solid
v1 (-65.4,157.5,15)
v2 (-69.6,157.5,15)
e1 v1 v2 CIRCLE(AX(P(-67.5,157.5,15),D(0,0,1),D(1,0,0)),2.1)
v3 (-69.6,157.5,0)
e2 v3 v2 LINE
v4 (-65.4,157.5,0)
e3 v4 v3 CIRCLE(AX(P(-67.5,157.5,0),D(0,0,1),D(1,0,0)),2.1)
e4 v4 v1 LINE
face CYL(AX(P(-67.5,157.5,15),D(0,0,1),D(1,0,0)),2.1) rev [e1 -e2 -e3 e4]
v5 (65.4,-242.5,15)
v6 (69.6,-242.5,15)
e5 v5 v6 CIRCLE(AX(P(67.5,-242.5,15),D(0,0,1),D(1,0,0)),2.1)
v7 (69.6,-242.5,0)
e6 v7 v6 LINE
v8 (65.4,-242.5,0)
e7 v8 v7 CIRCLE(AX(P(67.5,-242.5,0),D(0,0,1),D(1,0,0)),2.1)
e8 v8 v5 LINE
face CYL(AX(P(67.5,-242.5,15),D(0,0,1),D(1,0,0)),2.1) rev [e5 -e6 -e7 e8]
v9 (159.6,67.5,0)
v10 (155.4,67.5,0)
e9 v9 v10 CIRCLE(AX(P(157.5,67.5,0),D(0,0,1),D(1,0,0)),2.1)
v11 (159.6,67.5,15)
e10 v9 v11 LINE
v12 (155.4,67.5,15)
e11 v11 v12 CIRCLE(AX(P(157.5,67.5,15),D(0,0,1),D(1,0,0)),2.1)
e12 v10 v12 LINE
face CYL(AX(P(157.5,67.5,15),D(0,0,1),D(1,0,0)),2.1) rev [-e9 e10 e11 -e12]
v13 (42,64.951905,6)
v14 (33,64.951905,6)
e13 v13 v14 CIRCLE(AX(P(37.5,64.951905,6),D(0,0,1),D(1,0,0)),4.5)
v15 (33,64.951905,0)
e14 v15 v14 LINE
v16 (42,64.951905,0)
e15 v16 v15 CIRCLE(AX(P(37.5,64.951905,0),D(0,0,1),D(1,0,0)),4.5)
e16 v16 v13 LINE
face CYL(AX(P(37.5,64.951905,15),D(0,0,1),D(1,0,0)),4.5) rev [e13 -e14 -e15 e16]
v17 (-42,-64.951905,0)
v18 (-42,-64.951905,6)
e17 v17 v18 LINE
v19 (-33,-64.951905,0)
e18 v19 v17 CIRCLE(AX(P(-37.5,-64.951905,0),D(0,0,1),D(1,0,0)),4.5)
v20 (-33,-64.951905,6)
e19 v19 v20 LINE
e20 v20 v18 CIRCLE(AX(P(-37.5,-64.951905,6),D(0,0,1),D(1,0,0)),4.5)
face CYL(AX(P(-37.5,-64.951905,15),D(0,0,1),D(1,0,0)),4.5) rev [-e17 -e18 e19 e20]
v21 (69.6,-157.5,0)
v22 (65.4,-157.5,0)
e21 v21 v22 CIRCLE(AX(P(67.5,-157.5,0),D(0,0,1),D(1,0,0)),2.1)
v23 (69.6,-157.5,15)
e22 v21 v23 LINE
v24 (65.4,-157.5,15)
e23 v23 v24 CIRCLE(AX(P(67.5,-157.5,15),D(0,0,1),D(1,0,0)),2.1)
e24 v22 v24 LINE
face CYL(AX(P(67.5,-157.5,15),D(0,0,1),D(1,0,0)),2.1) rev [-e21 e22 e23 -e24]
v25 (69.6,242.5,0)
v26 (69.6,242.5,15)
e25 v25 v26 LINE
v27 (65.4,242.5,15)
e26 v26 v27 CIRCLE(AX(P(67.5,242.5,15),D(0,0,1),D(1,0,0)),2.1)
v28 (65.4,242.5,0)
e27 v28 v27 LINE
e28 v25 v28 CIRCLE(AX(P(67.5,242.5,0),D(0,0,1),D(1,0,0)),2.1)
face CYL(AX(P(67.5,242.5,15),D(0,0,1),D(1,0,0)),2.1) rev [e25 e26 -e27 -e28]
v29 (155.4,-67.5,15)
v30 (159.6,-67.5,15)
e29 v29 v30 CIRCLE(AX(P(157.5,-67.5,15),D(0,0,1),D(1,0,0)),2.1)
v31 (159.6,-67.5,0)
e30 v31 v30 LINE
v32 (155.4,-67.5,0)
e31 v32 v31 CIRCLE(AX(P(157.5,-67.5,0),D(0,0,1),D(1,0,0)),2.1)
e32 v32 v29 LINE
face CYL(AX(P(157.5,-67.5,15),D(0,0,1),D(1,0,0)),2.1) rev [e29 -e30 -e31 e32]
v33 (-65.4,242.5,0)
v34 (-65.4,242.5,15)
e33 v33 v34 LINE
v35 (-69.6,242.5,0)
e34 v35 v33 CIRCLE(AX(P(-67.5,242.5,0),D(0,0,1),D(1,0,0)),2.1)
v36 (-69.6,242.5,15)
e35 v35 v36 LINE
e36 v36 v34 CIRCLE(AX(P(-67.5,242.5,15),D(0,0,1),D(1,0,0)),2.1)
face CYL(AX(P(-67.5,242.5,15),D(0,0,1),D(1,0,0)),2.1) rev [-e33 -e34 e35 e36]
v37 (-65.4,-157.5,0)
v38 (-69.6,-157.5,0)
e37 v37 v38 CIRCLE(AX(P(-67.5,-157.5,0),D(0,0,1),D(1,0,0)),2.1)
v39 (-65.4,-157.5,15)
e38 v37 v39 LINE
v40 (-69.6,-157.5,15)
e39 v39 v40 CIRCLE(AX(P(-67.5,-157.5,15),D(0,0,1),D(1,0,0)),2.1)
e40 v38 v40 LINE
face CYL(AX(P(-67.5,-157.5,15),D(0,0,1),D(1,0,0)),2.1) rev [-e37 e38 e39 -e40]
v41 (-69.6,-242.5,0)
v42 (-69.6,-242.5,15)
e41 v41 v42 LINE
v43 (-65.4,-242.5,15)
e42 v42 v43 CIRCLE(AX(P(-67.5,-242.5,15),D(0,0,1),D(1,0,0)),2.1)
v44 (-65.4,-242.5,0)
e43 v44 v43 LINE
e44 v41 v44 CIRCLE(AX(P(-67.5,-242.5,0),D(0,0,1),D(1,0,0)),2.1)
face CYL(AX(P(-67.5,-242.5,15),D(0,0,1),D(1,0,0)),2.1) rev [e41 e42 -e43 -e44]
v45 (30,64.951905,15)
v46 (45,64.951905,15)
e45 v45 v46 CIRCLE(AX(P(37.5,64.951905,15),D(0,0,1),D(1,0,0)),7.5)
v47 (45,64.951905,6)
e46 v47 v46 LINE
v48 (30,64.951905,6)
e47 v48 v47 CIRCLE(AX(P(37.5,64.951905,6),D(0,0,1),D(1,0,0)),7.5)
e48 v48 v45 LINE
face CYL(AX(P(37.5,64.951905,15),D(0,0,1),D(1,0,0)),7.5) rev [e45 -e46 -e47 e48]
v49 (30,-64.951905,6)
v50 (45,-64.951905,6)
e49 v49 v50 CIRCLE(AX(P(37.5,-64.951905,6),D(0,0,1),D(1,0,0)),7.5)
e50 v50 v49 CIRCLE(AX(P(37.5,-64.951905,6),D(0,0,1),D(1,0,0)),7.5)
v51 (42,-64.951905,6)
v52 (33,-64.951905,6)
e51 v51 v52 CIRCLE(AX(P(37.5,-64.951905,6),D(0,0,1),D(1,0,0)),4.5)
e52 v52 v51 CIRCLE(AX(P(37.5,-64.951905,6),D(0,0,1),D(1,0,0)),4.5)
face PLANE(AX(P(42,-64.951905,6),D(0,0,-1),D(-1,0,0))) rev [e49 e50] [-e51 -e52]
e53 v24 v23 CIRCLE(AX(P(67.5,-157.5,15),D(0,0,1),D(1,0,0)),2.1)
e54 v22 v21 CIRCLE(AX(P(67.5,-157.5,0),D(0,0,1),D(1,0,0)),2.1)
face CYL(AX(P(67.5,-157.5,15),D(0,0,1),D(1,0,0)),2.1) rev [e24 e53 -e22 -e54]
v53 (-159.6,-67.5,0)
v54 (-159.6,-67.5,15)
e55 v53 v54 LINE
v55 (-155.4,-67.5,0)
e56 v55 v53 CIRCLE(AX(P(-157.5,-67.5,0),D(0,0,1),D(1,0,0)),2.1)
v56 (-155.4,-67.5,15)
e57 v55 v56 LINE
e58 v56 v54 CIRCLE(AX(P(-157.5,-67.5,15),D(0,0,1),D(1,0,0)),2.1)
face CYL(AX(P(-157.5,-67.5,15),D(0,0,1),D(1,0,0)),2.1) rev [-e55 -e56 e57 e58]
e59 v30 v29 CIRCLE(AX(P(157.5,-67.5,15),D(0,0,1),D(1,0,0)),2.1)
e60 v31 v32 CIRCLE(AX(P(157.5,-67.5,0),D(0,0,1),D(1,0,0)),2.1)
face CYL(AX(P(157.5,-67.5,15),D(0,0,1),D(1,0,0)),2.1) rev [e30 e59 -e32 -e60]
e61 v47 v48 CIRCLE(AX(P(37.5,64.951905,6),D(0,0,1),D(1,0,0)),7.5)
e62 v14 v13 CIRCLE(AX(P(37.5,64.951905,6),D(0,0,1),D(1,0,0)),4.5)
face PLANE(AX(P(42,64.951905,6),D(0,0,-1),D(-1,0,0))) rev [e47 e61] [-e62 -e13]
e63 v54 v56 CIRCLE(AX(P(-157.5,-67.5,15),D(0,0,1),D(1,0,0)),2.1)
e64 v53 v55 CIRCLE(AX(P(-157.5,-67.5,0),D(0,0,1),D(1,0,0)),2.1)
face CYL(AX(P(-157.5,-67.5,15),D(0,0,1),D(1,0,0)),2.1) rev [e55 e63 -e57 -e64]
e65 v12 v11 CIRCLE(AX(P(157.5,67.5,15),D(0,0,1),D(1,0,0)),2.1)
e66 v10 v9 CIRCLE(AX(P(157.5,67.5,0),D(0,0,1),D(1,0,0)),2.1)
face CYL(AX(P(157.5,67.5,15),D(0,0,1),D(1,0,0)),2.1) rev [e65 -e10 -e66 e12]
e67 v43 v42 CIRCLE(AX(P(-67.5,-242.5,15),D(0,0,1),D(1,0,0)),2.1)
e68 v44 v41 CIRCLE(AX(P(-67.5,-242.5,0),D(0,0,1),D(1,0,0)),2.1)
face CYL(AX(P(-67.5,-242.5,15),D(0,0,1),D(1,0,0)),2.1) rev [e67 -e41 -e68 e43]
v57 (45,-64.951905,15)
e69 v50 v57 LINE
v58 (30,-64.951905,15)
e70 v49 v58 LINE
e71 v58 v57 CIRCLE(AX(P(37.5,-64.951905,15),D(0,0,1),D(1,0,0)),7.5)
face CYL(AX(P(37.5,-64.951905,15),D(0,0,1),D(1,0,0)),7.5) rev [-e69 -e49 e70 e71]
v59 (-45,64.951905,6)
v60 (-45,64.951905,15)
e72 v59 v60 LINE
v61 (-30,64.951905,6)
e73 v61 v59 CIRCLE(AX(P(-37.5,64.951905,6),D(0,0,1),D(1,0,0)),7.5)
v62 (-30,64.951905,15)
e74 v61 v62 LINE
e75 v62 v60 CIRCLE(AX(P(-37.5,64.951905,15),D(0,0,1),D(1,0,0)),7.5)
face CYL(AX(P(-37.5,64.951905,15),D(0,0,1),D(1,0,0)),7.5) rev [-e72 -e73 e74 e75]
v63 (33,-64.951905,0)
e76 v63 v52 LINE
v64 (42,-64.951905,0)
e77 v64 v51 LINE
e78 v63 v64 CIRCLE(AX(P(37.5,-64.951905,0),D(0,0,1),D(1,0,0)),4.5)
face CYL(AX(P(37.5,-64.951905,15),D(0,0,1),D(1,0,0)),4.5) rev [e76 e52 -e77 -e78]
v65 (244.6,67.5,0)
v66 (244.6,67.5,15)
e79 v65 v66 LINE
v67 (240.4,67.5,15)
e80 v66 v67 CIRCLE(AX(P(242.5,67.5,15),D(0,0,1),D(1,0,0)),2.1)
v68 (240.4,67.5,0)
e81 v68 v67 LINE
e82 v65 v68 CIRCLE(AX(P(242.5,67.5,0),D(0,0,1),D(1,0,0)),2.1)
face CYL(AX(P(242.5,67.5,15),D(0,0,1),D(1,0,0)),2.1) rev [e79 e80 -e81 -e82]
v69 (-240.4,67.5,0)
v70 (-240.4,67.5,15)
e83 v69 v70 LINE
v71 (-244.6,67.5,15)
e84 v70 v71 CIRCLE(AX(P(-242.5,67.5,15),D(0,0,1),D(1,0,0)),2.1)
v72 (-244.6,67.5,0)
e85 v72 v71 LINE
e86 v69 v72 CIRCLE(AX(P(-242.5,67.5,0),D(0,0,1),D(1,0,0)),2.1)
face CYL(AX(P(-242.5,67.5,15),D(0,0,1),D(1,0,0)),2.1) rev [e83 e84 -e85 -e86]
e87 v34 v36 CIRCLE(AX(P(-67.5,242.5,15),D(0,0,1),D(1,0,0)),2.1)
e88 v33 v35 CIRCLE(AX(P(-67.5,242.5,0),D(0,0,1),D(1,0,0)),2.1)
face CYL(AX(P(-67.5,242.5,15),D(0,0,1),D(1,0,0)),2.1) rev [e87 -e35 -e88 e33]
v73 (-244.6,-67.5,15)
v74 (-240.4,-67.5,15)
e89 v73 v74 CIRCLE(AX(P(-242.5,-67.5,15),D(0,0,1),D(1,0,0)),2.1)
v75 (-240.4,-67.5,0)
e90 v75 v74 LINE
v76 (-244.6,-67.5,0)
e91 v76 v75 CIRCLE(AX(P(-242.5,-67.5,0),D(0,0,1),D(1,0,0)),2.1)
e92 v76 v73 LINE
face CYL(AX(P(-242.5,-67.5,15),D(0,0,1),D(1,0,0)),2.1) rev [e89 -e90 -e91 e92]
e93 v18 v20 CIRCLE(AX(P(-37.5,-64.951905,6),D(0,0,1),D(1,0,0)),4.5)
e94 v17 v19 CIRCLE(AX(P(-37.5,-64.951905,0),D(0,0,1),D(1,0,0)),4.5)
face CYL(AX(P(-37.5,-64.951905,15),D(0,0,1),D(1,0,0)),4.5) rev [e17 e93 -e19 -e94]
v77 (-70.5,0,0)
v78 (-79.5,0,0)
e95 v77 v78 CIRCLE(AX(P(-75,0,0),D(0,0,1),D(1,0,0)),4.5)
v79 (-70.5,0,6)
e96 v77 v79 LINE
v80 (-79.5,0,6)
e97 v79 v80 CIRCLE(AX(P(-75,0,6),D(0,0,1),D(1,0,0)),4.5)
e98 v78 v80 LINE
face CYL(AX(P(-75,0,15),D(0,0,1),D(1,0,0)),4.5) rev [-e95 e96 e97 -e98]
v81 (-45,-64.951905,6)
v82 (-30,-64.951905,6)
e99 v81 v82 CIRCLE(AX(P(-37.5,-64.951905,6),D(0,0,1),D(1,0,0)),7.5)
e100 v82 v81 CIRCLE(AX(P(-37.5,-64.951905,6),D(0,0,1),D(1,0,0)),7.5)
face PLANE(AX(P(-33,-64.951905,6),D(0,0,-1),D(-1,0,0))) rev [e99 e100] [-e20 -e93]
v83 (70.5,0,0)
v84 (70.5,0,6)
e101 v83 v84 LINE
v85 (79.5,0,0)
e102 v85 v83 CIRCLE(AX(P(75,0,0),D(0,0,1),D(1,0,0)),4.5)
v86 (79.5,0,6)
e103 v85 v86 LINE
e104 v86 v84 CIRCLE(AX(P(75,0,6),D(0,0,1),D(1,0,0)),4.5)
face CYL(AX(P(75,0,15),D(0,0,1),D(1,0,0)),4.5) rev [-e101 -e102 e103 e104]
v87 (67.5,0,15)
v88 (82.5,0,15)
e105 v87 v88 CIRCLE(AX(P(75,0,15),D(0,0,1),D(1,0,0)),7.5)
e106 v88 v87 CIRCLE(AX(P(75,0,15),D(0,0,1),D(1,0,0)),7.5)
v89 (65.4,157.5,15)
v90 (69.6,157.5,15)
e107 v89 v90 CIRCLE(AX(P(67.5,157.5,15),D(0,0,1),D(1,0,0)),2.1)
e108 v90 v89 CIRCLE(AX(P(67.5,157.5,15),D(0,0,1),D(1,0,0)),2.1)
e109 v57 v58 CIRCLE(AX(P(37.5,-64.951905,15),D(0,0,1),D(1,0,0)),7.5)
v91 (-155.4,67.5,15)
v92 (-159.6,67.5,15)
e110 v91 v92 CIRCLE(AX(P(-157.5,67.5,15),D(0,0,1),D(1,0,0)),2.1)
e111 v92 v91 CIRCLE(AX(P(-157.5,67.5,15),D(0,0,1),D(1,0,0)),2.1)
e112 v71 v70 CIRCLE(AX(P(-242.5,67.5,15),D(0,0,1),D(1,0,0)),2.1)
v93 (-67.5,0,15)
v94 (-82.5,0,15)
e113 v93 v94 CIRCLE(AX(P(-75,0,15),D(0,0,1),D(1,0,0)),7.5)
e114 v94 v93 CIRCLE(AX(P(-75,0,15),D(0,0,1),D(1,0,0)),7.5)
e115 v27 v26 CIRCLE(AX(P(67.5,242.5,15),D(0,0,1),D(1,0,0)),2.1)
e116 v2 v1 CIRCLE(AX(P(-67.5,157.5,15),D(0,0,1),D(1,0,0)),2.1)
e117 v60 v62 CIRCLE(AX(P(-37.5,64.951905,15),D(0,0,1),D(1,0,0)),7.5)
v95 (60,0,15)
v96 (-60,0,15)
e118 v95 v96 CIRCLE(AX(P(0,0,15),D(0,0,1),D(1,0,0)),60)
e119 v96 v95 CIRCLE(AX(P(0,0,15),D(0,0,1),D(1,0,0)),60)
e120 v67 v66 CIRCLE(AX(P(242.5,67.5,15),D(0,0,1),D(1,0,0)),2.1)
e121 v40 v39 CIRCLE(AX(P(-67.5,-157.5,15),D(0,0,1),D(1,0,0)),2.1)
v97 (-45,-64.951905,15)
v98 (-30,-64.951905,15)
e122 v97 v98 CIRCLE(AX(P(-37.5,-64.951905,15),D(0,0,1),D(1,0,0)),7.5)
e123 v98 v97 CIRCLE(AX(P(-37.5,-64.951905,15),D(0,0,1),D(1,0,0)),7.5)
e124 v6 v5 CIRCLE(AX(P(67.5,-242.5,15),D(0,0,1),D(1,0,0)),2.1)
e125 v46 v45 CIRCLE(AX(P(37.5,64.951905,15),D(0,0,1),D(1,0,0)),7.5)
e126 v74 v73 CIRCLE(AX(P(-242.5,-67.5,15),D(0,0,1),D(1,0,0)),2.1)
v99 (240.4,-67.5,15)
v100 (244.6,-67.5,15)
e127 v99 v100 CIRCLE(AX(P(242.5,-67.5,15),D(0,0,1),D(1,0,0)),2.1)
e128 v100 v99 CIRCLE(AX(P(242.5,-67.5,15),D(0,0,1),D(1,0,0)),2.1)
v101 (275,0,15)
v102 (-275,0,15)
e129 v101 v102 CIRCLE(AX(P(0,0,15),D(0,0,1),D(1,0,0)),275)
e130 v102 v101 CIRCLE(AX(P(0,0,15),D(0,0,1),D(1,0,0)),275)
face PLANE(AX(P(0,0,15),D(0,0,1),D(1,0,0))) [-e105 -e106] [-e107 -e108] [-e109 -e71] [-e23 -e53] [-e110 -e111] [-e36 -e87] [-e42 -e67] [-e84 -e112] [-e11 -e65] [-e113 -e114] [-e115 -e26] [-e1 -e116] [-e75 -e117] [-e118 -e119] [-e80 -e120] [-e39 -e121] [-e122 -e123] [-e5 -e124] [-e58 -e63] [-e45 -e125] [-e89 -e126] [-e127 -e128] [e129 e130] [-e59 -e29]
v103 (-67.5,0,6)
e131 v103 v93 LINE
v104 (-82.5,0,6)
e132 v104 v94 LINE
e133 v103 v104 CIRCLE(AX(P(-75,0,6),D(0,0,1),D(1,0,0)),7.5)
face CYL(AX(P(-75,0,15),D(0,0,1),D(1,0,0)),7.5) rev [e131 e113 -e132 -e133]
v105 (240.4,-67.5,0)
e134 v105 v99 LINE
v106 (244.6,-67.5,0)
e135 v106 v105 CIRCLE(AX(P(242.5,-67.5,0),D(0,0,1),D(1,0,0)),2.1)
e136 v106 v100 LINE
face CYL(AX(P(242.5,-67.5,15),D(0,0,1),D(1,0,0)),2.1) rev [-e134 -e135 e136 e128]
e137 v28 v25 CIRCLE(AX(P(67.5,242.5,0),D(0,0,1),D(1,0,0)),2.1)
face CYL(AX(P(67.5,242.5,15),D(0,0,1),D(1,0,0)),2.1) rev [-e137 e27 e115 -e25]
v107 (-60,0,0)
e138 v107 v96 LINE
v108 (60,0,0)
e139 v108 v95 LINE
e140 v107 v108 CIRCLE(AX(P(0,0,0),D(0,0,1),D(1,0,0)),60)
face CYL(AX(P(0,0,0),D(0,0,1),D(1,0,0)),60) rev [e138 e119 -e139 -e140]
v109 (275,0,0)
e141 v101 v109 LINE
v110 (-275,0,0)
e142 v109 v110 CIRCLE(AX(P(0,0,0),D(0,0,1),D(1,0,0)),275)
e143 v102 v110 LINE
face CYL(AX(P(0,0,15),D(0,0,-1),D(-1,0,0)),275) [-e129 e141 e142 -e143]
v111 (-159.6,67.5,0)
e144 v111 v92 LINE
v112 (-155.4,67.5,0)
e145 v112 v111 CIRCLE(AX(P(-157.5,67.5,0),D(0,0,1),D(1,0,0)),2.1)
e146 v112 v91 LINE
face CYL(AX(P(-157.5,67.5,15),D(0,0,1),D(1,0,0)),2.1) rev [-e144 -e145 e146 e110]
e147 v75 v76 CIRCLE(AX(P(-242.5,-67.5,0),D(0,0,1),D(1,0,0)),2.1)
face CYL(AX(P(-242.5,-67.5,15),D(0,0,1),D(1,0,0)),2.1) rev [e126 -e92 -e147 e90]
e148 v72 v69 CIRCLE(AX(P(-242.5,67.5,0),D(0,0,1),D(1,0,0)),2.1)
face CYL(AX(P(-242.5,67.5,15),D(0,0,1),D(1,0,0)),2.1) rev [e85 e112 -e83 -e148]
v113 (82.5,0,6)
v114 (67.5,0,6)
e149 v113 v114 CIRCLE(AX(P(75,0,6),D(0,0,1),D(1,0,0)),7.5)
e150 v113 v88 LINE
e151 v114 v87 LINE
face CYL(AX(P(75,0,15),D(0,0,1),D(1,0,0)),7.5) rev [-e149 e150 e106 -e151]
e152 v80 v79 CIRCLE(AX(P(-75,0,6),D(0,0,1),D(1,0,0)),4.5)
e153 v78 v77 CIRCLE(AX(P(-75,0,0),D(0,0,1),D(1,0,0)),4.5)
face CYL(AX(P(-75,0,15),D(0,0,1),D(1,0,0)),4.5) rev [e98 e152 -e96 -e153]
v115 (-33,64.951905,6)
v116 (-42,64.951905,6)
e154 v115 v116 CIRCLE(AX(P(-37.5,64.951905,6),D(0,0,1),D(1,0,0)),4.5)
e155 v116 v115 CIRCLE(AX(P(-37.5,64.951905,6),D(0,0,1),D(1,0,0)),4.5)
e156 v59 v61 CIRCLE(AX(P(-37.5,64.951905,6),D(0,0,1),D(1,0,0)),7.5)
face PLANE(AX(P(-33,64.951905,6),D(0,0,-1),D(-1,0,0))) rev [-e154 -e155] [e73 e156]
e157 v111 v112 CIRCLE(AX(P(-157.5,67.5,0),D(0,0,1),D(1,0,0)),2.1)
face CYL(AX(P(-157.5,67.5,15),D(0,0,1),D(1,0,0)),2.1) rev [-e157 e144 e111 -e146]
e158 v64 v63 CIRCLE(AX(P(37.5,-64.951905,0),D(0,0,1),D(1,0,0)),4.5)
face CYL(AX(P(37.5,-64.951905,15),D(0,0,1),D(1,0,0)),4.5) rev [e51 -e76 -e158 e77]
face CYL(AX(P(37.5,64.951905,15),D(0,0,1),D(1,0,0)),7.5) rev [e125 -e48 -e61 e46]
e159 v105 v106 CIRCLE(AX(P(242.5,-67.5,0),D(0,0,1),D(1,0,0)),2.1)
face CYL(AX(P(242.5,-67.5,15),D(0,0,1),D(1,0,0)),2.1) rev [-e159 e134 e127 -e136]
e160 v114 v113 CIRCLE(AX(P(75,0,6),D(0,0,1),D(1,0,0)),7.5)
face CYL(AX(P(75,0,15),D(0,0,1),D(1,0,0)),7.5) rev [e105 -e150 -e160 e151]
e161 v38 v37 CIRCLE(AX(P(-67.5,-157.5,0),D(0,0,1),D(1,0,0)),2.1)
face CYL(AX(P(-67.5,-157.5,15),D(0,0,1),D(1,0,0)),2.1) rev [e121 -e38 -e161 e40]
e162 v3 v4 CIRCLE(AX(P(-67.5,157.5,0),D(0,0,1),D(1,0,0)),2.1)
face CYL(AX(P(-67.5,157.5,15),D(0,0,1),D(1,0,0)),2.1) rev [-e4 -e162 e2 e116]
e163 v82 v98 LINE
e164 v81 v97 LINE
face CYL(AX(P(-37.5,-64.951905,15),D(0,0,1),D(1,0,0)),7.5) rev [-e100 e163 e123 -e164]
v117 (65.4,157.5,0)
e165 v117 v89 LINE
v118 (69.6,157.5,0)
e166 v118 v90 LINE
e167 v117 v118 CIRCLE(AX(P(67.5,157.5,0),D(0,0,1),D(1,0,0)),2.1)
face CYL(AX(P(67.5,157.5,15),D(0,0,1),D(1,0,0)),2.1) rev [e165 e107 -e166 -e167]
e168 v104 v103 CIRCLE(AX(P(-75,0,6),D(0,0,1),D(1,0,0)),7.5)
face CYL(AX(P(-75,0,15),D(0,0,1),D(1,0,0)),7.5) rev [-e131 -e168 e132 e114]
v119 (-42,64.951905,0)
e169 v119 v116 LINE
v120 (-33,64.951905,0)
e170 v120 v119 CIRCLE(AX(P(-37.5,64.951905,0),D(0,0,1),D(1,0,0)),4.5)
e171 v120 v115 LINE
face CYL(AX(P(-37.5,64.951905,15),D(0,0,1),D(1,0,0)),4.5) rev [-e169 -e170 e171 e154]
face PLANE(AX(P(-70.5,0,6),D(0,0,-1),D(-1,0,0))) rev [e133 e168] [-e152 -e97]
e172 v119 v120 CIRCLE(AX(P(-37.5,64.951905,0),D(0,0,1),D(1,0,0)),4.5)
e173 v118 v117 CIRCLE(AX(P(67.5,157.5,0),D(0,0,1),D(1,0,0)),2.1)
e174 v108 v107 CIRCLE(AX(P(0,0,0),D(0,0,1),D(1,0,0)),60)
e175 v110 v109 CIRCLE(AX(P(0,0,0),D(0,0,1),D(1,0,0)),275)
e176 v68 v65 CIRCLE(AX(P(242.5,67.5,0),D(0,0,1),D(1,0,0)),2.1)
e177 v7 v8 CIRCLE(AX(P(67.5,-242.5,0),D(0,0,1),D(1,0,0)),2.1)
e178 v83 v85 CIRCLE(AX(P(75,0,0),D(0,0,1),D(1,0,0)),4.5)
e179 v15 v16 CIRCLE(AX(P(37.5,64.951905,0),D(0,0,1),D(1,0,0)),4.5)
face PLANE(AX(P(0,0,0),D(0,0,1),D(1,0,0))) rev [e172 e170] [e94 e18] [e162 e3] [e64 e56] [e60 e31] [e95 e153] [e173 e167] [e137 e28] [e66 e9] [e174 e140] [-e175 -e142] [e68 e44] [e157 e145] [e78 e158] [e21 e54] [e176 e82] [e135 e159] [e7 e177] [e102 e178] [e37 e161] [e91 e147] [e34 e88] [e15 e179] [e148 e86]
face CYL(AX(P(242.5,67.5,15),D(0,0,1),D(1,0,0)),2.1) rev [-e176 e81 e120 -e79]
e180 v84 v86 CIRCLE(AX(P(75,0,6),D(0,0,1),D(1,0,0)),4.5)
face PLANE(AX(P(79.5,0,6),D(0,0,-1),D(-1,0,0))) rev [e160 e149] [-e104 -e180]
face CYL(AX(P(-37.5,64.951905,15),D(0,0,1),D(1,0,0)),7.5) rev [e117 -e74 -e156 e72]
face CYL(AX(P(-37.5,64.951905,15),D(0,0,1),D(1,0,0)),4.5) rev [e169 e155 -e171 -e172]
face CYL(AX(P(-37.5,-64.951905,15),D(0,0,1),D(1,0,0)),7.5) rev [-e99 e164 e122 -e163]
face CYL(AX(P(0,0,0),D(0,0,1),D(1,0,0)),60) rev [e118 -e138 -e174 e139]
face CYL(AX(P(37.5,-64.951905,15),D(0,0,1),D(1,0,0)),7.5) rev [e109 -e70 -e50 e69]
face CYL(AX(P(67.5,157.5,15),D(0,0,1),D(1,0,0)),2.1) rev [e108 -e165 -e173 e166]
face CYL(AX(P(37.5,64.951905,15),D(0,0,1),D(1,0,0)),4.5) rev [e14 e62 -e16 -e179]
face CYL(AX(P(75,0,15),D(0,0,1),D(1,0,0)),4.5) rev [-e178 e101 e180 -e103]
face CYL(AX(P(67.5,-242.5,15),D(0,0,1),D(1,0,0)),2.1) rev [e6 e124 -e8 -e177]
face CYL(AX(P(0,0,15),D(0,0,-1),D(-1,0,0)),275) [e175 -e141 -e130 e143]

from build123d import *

# Parameters (mm, degrees)
SKETCH1_R                                         = 275
BOSS_EXTRUDE1_DEPTH                               = 15
SKETCH2_R                                         = 60
CUT_EXTRUDE1_DEPTH                                = 390.197893108
M5_TAPPED_HOLE1_D                                 = 4.2
CIRPATTERN1_COUNT                                 = 4
HOLE_SIZE_BASED_SOCKET_HEAD_CAP_SCREW_D           = 9
HOLE_SIZE_BASED_SOCKET_HEAD_CAP_SCREW_CBORE_D     = 15
HOLE_SIZE_BASED_SOCKET_HEAD_CAP_SCREW_CBORE_DEPTH = 9
CIRPATTERN2_COUNT                                 = 6


with BuildPart() as part:
    # Sketch1 → Boss-Extrude1 (new body)
    with BuildSketch(Plane.XY):
        Circle(SKETCH1_R)
    extrude(amount=BOSS_EXTRUDE1_DEPTH)

    # Sketch2 → Cut-Extrude1 (cut, through all)
    with BuildSketch(Plane.XY.offset(15)):
        Circle(SKETCH2_R)
    extrude(amount=-CUT_EXTRUDE1_DEPTH, mode=Mode.SUBTRACT)

    # M5 Tapped Hole1 (through all)
    with Locations(Plane.XY.offset(15)):
        with Locations((67.5, 157.5), (67.5, 242.5), (-67.5, 157.5), (-67.5, 242.5)):
            m5_tapped_hole1 = Hole(M5_TAPPED_HOLE1_D / 2)

    # CirPattern1: M5 Tapped Hole1 ×4 about axis
    cirpattern1_axis = Axis((0, 0, 0), (0, 0, 1))
    for i in range(1, CIRPATTERN1_COUNT):
        add(m5_tapped_hole1.rotate(cirpattern1_axis, i * 360 / CIRPATTERN1_COUNT), mode=Mode.SUBTRACT)

    # Hole Size (%based) Socket Head Cap Screw Type1 (through all)
    with Locations(Plane.XY.offset(15)):
        with Locations((-37.5, 64.951905284)):
            hole_size_based_socket_head_cap_screw = CounterBoreHole(HOLE_SIZE_BASED_SOCKET_HEAD_CAP_SCREW_D / 2, HOLE_SIZE_BASED_SOCKET_HEAD_CAP_SCREW_CBORE_D / 2, HOLE_SIZE_BASED_SOCKET_HEAD_CAP_SCREW_CBORE_DEPTH)

    # CirPattern2: Hole Size (%based) Socket Head Cap Screw Type1 ×6 about axis
    cirpattern2_axis = Axis((0, 0, 0), (0, 0, 1))
    for i in range(1, CIRPATTERN2_COUNT):
        add(hole_size_based_socket_head_cap_screw.rotate(cirpattern2_axis, i * 360 / CIRPATTERN2_COUNT), mode=Mode.SUBTRACT)


solid = part.part
